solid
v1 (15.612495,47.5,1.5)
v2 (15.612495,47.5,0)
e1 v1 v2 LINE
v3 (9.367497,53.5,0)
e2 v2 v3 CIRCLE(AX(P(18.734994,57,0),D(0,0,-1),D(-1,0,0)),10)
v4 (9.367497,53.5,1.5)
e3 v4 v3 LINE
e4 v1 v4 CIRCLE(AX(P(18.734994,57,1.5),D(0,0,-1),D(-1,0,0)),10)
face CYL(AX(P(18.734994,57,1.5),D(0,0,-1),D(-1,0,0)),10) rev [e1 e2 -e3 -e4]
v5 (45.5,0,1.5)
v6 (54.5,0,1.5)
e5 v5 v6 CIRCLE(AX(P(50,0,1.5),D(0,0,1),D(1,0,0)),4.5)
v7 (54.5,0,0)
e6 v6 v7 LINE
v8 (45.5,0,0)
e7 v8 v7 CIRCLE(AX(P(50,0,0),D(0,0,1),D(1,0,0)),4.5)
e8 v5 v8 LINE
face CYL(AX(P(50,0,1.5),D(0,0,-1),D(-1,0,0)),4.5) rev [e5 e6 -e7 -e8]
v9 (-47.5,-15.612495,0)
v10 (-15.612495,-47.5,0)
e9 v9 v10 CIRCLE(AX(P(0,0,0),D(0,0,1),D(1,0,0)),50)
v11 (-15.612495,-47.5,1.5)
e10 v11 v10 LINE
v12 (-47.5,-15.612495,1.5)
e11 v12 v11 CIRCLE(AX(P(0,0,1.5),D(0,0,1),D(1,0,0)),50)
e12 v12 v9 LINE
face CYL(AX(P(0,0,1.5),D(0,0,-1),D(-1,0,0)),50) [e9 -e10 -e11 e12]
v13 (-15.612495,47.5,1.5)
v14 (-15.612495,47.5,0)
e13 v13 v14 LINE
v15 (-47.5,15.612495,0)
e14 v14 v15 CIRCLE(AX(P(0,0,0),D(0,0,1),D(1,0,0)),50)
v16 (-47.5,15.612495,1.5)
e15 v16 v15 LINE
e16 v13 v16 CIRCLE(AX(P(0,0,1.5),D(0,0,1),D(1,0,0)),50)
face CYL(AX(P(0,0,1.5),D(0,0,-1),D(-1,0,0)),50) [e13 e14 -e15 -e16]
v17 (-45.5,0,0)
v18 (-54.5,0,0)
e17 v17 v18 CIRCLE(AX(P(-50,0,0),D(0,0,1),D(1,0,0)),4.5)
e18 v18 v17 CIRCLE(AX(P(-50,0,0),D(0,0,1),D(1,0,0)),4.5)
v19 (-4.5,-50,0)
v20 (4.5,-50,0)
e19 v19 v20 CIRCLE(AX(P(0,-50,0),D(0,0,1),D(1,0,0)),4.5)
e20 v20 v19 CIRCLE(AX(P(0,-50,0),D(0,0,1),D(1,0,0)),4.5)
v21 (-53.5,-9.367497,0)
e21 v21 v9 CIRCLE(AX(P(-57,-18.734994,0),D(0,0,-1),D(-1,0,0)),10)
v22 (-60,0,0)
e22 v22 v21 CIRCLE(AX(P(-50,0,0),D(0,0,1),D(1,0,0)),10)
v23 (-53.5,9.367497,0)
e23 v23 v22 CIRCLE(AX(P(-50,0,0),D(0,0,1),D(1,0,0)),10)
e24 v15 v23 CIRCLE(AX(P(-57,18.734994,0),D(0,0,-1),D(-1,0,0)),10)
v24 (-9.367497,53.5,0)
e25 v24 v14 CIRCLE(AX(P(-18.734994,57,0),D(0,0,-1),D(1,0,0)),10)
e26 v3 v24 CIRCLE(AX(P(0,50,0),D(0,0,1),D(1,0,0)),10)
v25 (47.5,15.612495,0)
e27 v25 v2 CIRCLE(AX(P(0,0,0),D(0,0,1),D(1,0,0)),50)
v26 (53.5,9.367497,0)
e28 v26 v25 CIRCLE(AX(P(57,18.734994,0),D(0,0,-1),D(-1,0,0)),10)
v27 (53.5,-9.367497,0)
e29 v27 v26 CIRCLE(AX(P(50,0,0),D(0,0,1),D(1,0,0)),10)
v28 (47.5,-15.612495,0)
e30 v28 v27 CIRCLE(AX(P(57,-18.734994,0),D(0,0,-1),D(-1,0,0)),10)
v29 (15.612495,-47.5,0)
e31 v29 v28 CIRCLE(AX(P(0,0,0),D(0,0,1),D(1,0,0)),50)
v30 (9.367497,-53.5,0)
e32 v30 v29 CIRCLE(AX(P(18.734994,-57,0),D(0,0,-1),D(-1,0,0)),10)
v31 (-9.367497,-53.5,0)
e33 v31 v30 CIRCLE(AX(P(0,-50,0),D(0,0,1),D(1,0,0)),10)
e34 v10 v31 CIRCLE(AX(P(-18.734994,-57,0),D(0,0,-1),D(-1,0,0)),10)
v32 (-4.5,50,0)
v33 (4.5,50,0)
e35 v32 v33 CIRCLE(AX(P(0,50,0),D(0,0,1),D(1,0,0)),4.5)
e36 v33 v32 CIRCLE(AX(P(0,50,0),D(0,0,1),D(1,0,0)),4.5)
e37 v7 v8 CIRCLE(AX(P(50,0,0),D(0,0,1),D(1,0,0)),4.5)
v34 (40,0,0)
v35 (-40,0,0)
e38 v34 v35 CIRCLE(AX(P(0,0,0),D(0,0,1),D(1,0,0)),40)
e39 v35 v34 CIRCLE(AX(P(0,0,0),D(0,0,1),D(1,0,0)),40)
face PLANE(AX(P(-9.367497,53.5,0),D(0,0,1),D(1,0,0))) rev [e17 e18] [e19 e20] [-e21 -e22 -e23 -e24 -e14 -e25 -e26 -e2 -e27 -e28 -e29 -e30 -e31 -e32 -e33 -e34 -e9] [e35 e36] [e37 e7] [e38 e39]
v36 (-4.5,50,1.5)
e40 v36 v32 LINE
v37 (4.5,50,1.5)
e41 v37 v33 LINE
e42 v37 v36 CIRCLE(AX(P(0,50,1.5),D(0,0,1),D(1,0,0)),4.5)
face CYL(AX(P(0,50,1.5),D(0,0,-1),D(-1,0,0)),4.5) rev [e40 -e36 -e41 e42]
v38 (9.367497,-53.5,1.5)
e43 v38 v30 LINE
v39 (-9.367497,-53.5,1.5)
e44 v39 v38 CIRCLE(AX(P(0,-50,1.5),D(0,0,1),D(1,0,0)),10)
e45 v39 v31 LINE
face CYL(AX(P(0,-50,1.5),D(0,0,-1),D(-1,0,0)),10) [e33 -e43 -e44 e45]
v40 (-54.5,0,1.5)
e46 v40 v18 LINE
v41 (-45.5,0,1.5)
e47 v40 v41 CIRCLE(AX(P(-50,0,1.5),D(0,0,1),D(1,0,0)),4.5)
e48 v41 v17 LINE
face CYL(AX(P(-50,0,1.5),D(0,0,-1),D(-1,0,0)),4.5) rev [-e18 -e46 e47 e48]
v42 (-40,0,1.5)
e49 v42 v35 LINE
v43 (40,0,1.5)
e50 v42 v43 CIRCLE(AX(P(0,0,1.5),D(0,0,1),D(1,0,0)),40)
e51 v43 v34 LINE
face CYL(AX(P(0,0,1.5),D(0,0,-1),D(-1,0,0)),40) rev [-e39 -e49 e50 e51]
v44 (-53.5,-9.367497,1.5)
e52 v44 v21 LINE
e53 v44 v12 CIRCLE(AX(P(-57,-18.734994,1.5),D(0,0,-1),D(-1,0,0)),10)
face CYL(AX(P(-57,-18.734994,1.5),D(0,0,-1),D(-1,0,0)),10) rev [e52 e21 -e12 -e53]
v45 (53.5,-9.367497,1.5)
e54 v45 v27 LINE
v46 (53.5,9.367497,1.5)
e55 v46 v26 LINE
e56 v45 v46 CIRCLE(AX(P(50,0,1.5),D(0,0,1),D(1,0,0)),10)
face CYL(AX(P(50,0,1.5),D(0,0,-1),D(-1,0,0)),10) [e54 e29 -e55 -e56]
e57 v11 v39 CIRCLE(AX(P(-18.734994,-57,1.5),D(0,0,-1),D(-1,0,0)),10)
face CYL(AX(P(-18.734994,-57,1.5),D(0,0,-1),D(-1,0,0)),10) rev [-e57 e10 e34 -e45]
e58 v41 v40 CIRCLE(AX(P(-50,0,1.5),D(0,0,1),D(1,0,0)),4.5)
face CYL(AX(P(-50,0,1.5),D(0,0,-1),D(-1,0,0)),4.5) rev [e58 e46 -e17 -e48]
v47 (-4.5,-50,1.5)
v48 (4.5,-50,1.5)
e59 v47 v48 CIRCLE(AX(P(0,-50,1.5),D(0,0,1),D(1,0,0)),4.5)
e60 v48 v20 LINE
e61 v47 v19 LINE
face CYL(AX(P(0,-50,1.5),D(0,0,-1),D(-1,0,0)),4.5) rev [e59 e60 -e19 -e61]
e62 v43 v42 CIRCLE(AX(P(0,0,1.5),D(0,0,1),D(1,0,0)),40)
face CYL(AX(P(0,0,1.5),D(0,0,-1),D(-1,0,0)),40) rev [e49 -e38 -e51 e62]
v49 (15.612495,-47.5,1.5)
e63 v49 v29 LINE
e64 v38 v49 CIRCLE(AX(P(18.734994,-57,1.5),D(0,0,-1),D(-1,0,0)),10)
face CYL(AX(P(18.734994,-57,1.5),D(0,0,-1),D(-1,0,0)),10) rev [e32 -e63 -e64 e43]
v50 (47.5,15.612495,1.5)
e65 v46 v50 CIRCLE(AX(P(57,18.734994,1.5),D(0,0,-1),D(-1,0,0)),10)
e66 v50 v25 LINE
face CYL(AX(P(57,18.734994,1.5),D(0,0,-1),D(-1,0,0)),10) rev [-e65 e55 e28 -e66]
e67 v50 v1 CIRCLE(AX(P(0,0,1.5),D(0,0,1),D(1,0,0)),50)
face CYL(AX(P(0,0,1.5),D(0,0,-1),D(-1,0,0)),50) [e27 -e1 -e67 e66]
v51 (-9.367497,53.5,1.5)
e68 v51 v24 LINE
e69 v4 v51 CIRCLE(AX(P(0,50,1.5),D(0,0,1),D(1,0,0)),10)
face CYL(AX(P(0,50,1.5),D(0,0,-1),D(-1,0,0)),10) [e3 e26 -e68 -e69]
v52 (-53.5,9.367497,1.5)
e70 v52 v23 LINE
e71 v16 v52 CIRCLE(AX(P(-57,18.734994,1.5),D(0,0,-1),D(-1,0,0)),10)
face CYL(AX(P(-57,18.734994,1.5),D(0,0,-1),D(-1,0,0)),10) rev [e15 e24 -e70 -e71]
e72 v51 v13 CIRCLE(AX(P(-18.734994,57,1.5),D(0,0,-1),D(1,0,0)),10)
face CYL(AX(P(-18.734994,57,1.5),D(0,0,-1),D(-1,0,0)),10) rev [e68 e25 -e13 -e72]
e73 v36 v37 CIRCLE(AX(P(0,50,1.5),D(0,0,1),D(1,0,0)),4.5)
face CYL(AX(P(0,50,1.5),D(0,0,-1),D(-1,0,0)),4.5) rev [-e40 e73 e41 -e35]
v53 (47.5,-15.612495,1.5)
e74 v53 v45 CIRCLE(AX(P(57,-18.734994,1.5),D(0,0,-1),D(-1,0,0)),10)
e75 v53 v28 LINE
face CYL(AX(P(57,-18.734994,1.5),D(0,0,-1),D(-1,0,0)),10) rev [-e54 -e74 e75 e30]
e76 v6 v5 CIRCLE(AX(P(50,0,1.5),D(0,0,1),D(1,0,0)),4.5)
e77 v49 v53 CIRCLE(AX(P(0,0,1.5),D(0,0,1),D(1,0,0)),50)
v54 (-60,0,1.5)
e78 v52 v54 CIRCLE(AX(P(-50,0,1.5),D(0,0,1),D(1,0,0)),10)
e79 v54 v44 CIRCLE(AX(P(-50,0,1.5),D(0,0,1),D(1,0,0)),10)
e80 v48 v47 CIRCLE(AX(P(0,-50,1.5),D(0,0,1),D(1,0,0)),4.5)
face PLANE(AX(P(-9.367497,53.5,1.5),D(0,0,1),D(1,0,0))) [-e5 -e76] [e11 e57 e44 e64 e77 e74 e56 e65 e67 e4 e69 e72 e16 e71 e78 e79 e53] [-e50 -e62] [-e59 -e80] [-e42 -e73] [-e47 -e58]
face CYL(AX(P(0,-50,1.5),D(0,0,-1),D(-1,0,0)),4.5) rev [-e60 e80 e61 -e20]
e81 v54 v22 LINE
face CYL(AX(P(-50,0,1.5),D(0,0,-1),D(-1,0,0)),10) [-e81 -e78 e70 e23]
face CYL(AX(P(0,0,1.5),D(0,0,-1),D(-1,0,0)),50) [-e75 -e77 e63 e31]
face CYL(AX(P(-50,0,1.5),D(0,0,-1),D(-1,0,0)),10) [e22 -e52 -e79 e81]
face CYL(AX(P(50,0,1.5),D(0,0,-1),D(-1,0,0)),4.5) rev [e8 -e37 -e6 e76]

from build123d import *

# Parameters (mm, degrees)
SKETCH_1_R      = 40
SKETCH_1_R_2    = 4.5
EXTRUDE_1_DEPTH = 1.5


with BuildPart() as part:
    # 草图1 → 凸台-拉伸1 (new body)
    with BuildSketch(Plane.XY):
        with BuildLine():
            ThreePointArc((15.612494996, -47.5), (35.355339059, -35.355339059), (47.5, -15.612494996))
            ThreePointArc((47.5, -15.612494996), (49.788897449, -11.806790765), (53.5, -9.367496998))
            ThreePointArc((53.5, -9.367496998), (60, 0), (53.5, 9.367496998))
            ThreePointArc((53.5, 9.367496998), (49.788897449, 11.806790765), (47.5, 15.612494996))
            ThreePointArc((47.5, 15.612494996), (35.355339059, 35.355339059), (15.612494996, 47.5))
            ThreePointArc((15.612494996, 47.5), (11.806790765, 49.788897449), (9.367496998, 53.5))
            ThreePointArc((9.367496998, 53.5), (0, 60), (-9.367496998, 53.5))
            ThreePointArc((-9.367496998, 53.5), (-11.806790765, 49.788897449), (-15.612494996, 47.5))
            ThreePointArc((-15.612494996, 47.5), (-35.355339059, 35.355339059), (-47.5, 15.612494996))
            ThreePointArc((-47.5, 15.612494996), (-49.788897449, 11.806790765), (-53.5, 9.367496998))
            ThreePointArc((-53.5, 9.367496998), (-60, 0), (-53.5, -9.367496998))
            ThreePointArc((-53.5, -9.367496998), (-49.788897449, -11.806790765), (-47.5, -15.612494996))
            ThreePointArc((-47.5, -15.612494996), (-35.355339059, -35.355339059), (-15.612494996, -47.5))
            ThreePointArc((-15.612494996, -47.5), (-11.806790765, -49.788897449), (-9.367496998, -53.5))
            ThreePointArc((-9.367496998, -53.5), (0, -60), (9.367496998, -53.5))
            ThreePointArc((9.367496998, -53.5), (11.806790765, -49.788897449), (15.612494996, -47.5))
        make_face()
        Circle(SKETCH_1_R, mode=Mode.SUBTRACT)
        with Locations((0, 50)):
            Circle(SKETCH_1_R_2, mode=Mode.SUBTRACT)
        with Locations((-50, 0)):
            Circle(SKETCH_1_R_2, mode=Mode.SUBTRACT)
        with Locations((0, -50)):
            Circle(SKETCH_1_R_2, mode=Mode.SUBTRACT)
        with Locations((50, 0)):
            Circle(SKETCH_1_R_2, mode=Mode.SUBTRACT)
    extrude(amount=EXTRUDE_1_DEPTH)


solid = part.part
